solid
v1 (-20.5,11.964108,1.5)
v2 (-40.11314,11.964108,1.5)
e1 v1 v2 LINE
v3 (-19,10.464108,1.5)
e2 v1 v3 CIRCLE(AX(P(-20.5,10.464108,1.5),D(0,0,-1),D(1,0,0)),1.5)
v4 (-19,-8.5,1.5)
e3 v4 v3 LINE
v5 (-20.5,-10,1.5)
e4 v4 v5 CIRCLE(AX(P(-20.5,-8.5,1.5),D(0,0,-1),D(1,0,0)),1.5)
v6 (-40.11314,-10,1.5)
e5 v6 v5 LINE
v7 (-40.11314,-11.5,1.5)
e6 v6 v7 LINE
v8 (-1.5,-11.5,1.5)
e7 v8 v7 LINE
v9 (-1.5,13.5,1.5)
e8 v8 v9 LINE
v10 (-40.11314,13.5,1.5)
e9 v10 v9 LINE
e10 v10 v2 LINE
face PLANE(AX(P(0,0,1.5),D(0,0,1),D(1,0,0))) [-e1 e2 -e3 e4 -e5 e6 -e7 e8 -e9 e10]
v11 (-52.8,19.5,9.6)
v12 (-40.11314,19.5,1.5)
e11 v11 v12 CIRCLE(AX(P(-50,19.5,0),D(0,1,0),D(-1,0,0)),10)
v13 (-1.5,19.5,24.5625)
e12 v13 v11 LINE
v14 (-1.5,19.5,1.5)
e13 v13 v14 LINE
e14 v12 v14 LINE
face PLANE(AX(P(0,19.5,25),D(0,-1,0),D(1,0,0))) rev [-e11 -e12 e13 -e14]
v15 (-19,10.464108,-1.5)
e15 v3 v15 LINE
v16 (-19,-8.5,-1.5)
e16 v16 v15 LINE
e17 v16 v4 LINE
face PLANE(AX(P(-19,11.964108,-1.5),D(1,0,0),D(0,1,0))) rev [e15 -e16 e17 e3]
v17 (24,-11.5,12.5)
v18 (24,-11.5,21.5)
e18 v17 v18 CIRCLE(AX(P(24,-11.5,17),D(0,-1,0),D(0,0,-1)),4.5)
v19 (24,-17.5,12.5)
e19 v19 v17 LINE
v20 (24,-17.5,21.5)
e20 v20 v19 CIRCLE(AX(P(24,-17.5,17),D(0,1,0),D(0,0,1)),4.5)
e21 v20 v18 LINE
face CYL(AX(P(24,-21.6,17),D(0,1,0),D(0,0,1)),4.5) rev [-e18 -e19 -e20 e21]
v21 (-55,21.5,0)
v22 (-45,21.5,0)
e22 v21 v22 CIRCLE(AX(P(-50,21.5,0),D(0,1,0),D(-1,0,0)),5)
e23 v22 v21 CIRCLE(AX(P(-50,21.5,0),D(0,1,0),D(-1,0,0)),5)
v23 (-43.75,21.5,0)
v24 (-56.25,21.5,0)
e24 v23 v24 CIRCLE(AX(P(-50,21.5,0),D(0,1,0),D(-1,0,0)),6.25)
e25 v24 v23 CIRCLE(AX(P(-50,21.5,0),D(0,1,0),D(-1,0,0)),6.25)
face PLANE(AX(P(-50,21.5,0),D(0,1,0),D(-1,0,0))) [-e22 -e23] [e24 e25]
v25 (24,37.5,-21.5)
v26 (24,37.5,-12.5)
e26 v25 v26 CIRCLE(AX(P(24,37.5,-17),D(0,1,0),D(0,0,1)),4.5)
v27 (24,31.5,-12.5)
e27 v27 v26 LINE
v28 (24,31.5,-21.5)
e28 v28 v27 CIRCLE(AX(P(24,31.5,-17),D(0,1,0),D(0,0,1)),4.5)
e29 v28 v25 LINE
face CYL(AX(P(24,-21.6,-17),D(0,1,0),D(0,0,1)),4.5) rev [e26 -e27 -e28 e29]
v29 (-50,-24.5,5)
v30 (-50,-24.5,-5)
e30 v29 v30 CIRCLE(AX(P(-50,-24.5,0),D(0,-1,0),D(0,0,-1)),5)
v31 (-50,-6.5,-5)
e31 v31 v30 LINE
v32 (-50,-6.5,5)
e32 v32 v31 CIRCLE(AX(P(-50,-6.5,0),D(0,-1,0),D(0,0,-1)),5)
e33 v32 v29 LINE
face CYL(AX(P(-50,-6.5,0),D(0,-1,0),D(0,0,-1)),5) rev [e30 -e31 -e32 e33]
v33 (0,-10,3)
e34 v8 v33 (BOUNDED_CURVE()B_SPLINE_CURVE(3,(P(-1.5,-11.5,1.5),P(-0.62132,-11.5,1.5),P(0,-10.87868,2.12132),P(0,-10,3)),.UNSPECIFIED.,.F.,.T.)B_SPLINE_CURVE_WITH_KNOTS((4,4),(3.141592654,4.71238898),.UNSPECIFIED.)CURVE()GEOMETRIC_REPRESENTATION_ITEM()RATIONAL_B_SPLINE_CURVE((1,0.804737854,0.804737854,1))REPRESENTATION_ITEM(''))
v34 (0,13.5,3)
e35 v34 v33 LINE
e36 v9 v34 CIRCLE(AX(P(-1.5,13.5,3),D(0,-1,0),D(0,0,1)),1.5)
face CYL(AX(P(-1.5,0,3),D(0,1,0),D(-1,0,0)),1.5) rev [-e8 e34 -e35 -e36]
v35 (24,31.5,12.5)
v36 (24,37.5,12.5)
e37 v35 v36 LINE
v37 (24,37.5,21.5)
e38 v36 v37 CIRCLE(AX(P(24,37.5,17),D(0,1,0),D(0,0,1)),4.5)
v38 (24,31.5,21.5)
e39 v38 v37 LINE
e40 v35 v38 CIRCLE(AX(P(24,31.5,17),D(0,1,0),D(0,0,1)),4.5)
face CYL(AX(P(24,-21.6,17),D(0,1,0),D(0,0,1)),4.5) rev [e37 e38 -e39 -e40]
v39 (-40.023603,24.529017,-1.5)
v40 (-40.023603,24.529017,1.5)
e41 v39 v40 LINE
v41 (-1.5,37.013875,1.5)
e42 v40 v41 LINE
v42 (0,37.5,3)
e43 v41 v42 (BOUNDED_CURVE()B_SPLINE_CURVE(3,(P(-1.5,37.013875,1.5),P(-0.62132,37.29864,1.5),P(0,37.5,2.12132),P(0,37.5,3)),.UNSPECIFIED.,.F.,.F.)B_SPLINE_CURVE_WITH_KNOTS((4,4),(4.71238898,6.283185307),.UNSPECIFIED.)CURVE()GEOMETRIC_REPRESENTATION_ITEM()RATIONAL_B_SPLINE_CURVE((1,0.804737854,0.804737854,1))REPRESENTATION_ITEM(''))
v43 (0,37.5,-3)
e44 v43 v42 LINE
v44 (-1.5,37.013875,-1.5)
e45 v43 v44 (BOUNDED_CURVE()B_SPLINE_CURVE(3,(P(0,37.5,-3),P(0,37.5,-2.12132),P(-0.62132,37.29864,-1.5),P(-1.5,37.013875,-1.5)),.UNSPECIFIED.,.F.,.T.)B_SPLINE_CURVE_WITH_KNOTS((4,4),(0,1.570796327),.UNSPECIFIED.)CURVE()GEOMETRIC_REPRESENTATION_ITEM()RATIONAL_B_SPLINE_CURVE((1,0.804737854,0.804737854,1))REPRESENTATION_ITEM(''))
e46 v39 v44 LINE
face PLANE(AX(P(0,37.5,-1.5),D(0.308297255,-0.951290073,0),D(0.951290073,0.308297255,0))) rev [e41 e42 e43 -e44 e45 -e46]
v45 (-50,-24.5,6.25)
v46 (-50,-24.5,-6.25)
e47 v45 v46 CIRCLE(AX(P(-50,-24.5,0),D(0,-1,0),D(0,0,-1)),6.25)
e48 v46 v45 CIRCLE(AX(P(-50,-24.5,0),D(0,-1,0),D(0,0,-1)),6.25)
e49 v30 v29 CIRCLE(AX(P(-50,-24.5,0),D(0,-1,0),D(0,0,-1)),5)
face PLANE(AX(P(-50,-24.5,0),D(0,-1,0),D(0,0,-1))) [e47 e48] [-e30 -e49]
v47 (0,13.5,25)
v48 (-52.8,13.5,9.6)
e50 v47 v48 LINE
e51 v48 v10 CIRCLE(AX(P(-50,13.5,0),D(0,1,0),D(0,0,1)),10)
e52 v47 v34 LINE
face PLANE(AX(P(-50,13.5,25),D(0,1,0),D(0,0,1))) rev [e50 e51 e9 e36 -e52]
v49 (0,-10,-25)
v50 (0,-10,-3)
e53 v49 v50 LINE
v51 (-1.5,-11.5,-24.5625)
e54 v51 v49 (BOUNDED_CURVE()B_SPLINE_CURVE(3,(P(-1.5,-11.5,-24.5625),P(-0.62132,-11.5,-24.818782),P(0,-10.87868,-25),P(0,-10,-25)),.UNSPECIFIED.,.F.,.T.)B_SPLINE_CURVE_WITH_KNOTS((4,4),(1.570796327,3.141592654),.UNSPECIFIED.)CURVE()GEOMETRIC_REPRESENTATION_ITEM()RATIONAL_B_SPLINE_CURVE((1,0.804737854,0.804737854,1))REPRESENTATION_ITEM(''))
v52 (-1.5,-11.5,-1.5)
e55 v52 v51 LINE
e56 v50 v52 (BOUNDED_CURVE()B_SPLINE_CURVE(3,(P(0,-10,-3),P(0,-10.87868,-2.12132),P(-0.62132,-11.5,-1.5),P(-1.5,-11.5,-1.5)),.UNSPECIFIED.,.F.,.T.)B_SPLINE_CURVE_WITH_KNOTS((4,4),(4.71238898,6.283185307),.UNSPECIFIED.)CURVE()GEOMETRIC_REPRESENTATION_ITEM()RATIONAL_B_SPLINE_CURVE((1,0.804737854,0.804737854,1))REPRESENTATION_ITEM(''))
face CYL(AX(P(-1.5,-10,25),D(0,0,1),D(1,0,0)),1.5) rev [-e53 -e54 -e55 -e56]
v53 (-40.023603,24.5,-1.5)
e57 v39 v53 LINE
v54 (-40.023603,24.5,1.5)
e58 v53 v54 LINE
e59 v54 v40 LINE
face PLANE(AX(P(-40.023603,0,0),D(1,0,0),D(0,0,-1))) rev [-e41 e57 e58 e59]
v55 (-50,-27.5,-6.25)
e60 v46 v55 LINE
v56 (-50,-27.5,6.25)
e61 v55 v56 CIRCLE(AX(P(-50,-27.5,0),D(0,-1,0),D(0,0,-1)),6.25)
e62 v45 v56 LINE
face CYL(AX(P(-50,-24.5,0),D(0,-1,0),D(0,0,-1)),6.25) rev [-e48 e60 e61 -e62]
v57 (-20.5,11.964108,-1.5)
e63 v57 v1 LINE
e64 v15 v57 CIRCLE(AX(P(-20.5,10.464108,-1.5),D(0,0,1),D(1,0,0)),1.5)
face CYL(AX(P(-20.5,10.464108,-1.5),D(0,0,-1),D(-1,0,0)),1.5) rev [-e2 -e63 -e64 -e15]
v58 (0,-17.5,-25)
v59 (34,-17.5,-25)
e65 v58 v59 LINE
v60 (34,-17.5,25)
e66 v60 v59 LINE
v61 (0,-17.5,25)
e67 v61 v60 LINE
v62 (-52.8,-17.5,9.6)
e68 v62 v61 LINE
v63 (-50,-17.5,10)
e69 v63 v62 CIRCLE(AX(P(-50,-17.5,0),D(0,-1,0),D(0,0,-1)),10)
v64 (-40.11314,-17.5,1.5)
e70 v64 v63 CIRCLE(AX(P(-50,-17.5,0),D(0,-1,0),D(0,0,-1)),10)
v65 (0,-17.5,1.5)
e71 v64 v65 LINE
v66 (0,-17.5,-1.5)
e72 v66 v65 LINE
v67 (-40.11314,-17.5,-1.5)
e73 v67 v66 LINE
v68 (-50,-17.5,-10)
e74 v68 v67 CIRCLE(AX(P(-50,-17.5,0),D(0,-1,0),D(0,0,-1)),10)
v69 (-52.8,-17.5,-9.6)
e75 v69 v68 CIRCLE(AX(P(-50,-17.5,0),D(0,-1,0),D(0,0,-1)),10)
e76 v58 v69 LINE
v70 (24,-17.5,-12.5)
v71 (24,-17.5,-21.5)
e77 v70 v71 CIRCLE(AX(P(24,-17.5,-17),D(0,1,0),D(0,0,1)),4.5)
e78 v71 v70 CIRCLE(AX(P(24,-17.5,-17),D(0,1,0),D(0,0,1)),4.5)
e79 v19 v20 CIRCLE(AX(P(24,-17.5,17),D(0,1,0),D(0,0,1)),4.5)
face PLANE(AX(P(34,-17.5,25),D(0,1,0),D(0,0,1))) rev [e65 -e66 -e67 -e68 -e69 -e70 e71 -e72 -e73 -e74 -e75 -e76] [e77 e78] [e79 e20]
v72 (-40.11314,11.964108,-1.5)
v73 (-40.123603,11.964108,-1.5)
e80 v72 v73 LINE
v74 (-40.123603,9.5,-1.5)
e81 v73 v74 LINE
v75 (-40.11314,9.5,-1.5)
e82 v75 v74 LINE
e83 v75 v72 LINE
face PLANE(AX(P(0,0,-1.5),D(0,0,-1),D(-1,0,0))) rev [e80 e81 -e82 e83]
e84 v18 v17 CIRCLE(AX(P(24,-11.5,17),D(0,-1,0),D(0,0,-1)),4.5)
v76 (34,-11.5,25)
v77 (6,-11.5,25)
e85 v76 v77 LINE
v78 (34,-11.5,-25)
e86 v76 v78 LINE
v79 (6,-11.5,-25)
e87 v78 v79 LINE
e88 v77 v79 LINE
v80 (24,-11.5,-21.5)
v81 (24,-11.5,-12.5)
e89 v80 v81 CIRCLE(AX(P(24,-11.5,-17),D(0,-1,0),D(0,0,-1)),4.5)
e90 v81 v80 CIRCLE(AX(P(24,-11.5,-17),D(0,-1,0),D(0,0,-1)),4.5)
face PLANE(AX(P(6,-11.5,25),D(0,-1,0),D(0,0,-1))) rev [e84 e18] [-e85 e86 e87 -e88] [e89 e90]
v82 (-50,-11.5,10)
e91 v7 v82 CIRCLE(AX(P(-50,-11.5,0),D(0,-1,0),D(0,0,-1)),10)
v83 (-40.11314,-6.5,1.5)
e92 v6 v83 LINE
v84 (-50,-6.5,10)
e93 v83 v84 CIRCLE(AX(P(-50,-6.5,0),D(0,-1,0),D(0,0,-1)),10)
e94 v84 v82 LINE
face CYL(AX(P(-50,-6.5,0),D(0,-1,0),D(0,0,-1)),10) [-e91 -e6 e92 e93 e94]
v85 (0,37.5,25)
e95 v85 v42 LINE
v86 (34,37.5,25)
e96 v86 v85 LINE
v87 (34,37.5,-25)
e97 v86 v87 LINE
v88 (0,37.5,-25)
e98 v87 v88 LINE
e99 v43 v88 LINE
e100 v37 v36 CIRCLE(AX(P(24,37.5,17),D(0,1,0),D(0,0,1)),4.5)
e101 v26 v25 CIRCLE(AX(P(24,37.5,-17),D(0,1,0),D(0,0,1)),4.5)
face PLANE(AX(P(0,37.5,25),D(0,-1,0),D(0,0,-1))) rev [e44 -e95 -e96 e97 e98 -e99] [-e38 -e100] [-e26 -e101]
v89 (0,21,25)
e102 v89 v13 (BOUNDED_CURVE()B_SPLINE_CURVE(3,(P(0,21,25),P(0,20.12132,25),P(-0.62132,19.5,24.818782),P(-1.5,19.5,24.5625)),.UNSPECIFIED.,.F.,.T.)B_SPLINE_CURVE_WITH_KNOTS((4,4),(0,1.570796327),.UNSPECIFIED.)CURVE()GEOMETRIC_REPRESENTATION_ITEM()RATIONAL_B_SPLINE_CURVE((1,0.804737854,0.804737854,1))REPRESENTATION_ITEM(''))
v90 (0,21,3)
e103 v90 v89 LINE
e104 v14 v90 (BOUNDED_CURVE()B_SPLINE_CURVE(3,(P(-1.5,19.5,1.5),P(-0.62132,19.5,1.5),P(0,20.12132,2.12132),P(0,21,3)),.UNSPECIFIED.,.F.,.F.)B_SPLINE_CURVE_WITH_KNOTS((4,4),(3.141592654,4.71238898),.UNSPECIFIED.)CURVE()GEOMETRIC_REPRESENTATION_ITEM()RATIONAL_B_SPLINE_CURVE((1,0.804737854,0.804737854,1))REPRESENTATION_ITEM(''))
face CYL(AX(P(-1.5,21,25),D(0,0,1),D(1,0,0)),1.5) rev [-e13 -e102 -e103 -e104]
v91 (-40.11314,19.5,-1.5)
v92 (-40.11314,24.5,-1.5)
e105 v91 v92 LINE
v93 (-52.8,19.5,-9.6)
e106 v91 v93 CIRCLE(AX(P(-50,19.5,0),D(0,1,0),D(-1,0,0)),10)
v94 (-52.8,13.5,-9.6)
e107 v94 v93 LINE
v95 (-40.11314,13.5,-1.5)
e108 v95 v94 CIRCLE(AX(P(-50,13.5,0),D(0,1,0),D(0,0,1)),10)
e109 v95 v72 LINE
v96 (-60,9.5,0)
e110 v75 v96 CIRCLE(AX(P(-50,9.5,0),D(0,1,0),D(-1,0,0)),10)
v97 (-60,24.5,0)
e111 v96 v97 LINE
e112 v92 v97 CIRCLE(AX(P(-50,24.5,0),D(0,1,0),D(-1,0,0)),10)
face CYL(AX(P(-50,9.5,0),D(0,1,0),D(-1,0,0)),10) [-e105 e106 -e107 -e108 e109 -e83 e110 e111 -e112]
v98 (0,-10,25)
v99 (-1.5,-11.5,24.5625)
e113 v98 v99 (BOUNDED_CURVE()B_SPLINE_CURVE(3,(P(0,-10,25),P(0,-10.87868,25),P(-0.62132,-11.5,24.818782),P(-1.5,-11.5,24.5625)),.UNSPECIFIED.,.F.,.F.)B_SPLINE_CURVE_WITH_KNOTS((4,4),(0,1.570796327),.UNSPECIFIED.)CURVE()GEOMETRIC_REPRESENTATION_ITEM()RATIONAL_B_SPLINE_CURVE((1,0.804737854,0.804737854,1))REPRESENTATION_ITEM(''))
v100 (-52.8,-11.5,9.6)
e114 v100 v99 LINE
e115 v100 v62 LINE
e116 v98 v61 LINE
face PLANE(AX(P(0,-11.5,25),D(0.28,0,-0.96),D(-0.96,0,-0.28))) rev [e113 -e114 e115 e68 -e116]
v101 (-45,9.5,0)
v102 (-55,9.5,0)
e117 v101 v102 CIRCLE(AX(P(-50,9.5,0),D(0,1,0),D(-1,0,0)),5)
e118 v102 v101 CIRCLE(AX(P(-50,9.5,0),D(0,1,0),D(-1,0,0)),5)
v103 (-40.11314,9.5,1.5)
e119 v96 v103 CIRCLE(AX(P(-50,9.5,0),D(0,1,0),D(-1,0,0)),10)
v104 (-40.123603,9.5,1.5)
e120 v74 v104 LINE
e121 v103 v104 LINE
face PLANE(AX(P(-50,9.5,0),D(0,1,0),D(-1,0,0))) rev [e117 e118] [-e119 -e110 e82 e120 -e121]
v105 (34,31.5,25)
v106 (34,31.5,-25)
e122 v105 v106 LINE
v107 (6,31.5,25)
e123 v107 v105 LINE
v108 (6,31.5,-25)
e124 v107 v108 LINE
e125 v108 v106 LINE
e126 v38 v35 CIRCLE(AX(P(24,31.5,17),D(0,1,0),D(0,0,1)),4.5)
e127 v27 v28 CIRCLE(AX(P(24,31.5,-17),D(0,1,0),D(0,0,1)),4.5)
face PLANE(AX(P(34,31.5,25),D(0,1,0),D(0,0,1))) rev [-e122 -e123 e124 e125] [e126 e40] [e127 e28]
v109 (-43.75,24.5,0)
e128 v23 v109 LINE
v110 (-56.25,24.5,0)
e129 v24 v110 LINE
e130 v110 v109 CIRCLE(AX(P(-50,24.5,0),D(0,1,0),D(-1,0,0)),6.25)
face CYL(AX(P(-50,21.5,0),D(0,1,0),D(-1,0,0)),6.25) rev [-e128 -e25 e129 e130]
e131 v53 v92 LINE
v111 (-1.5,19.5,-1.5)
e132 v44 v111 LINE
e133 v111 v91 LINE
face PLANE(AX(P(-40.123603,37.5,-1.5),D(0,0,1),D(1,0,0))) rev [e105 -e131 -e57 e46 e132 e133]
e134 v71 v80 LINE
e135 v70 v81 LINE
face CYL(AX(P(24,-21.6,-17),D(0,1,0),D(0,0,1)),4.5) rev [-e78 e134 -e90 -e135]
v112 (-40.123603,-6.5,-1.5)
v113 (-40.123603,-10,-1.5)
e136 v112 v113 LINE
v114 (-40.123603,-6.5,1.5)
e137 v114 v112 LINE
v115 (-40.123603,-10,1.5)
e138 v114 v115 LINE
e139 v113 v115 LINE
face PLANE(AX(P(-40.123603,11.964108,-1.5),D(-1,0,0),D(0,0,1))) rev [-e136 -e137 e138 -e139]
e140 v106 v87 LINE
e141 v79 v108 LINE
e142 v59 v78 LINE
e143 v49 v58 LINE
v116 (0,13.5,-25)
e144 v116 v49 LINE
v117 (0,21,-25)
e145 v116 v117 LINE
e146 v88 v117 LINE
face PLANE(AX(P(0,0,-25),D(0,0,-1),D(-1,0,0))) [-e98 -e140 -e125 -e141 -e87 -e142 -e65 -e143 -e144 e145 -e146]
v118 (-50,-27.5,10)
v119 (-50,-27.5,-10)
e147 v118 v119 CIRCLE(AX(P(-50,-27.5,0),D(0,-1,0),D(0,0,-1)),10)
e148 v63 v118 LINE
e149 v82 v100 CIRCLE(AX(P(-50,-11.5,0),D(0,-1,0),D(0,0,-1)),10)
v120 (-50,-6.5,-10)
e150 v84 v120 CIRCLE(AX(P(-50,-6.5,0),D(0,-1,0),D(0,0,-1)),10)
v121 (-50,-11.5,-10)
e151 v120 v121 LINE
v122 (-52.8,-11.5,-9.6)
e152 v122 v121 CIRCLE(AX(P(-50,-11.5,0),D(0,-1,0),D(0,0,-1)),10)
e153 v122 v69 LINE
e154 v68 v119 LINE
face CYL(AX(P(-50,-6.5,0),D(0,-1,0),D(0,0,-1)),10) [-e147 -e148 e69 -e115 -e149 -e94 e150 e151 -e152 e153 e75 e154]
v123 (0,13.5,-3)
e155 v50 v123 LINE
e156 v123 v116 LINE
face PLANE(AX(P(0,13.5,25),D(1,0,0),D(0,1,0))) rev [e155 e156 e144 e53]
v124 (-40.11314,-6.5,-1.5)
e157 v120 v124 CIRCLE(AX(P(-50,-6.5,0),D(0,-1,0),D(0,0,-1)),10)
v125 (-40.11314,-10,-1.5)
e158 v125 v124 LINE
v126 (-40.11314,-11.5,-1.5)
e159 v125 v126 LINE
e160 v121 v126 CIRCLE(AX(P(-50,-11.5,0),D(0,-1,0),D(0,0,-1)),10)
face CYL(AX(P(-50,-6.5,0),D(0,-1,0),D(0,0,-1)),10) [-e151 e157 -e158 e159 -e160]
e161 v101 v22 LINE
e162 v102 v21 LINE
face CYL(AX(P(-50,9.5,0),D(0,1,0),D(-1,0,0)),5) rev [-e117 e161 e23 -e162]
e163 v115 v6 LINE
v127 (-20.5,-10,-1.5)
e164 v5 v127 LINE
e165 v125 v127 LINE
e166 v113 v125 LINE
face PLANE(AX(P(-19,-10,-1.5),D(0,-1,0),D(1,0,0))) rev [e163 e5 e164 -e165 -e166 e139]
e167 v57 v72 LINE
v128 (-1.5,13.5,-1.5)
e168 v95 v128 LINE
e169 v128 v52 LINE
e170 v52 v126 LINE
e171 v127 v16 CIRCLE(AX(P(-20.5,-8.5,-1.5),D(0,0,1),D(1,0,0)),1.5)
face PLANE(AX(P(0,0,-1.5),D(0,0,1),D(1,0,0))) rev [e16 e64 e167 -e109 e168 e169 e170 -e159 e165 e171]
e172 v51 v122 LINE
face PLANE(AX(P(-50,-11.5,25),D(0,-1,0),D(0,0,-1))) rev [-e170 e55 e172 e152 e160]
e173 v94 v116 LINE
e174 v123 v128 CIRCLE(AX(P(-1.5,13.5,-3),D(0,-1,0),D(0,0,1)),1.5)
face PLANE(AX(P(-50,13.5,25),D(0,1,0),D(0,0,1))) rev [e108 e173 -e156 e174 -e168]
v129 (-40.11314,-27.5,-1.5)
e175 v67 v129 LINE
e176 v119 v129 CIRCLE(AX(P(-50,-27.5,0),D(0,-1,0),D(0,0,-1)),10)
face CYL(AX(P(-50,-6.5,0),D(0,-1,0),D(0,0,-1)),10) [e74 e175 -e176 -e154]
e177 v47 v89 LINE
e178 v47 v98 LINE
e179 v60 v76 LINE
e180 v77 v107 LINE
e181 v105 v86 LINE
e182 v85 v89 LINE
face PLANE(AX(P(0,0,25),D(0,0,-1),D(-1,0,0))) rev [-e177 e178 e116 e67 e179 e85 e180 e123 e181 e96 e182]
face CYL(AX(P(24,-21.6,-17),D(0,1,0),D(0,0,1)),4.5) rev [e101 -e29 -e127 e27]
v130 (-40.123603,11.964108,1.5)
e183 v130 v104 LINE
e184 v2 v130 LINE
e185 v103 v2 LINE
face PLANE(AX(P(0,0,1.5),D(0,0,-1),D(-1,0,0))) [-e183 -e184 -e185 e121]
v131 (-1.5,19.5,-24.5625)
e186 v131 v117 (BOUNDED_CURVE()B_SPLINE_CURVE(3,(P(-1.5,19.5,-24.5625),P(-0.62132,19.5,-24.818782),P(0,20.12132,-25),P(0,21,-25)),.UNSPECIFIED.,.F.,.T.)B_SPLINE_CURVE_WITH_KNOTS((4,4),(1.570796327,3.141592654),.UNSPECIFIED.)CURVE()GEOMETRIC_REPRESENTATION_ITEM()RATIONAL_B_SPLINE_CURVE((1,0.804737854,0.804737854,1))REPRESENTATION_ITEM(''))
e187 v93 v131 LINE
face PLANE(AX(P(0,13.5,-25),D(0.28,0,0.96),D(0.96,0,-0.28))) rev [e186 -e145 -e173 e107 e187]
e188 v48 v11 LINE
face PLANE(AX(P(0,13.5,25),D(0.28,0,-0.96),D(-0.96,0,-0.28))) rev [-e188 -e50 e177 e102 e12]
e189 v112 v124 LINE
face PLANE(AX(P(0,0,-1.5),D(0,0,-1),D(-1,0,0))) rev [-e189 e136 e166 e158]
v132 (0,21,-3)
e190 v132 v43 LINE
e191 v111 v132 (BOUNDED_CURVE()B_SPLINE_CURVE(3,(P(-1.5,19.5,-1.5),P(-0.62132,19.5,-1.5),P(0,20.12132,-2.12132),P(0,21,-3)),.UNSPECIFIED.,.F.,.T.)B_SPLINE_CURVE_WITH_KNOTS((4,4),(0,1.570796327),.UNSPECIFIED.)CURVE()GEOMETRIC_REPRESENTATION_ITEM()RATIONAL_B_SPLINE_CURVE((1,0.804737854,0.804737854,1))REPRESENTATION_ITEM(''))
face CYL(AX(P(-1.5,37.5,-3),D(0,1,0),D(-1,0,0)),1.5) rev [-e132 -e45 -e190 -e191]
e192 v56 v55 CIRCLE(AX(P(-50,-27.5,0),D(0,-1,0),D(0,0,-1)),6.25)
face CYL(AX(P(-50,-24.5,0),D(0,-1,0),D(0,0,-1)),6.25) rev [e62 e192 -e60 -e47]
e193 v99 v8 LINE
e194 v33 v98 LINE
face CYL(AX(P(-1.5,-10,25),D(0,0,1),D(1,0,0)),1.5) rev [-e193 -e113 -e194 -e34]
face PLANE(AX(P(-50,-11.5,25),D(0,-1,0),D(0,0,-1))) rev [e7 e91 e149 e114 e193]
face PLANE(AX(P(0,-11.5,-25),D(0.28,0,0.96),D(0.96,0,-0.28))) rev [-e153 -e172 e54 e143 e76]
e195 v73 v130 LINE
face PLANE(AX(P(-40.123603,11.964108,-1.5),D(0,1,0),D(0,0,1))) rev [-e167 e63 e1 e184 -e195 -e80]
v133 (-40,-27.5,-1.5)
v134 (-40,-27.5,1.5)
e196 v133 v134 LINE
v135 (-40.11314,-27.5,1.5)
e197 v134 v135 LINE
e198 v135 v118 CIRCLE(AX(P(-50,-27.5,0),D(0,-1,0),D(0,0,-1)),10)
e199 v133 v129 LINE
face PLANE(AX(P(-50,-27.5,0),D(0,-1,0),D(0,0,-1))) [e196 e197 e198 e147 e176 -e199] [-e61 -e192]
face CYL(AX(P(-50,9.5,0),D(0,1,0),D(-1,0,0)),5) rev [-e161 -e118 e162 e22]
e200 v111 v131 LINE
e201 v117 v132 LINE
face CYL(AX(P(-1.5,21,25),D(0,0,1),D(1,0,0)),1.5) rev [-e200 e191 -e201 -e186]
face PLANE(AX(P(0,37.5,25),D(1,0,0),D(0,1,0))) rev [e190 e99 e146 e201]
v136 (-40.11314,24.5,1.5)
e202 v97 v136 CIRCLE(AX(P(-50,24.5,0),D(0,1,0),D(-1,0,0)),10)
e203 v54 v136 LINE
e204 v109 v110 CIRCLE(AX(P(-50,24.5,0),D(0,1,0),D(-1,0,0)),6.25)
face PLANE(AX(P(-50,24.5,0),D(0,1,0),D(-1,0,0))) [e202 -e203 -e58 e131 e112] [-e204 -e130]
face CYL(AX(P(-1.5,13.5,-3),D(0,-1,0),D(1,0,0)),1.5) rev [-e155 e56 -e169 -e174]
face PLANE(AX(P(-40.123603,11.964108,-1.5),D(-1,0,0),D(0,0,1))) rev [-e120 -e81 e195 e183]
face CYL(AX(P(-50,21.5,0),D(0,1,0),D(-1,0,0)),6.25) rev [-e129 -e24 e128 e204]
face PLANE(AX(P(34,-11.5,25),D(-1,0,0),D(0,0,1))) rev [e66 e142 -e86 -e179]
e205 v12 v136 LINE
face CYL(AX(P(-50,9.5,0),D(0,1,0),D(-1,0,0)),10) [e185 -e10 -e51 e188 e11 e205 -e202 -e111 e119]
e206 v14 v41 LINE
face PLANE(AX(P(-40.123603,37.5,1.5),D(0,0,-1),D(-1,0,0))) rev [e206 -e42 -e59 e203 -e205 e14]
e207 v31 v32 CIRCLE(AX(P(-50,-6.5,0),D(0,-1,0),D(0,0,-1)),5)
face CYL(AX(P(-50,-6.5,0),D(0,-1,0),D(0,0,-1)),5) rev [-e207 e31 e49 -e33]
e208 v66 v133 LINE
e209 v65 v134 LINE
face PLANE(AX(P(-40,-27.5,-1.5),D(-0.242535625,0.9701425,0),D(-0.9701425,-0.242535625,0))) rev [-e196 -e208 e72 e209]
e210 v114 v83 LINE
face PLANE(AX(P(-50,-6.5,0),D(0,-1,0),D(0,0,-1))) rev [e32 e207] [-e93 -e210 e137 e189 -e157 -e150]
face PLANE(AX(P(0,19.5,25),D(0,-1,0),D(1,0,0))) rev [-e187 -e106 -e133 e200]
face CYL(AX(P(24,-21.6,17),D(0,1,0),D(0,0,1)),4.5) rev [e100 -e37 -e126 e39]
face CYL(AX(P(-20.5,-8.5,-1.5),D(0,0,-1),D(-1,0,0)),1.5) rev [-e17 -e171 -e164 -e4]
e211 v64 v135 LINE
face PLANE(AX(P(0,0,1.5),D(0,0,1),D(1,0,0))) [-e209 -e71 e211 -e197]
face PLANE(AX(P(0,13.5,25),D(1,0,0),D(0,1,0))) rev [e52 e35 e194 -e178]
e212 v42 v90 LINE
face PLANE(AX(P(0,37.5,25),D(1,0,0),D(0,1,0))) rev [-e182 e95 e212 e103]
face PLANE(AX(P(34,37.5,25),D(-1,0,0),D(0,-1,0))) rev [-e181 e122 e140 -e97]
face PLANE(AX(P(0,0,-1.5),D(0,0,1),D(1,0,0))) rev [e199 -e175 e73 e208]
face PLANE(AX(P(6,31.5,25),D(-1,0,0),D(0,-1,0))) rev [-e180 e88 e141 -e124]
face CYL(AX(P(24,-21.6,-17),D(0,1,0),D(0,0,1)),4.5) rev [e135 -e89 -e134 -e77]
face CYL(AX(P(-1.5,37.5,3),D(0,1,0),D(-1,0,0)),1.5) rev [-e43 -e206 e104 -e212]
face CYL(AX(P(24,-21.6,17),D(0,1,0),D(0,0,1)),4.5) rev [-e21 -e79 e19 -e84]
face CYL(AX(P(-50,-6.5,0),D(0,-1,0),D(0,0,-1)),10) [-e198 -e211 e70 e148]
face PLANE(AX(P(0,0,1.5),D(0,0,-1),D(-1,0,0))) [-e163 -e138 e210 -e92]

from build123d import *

# Parameters (mm, degrees)
U_CHANNEL_BASE_DEPTH             = 25
UPPER_LUG_BOSS_SKETCH_20_R       = 10
UPPER_LUG_BOSS_20_DEPTH          = 10
UPPER_START                      = 5
UPPER_LUG_PAD_SKETCH_R           = 10
UPPER_LUG_PAD_DEPTH              = 5
UPPER_COUNTERBORE_SKETCH_12_5_R  = 6.25
UPPER_COUNTERBORE_12_5_DEPTH     = 3
UPPER_LUG_HOLE_SKETCH_10_R       = 5
UPPER_LUG_HOLE_10_DEPTH          = 12
LOWER_START                      = -11
LOWER_LUG_PAD_SKETCH_R           = 10
LOWER_LUG_PAD_DEPTH              = 11
LOWER_LUG_BOSS_SKETCH_20_R       = 10
LOWER_LUG_BOSS_20_DEPTH          = 10
LOWER_START_2                    = -3
LOWER_COUNTERBORE_SKETCH_12_5_R  = 6.25
LOWER_COUNTERBORE_12_5_DEPTH     = 3
LOWER_START_3                    = -18
LOWER_LUG_HOLE_SKETCH_10_R       = 5
LOWER_LUG_HOLE_10_DEPTH          = 18
UPPER_GUSSET_DEPTH               = 6
UPPER_GUSSET_TRIM_DEPTH          = 6
LOWER_GUSSET_DEPTH               = 6
LOWER_GUSSET_TRIM_DEPTH          = 6
BACK_PLATE_DEPTH                 = 1.5
BACK_PLATE_LOWER_RELIEF_DEPTH    = 3
LOWER_LUG_RELIEF_SKETCH_W        = 3
LOWER_LUG_RELIEF_SKETCH_H        = 5
LOWER_LUG_RELIEF_DEPTH           = 3
BACK_PLATE_UPPER_RELIEF_SKETCH_W = 40.123603225
BACK_PLATE_UPPER_RELIEF_SKETCH_H = 13
BACK_PLATE_UPPER_RELIEF_DEPTH    = 3
BACK_PLATE_EDGE_TRIM_SKETCH_W    = 21.123603225
BACK_PLATE_EDGE_TRIM_SKETCH_H    = 21.964107992
BACK_PLATE_EDGE_TRIM_DEPTH       = 3
WEB_SKETCH_W                     = 40.123603225
WEB_SKETCH_H                     = 3
WEB_DEPTH                        = 18
WEB_CHAMFER_CUT_DEPTH            = 3
WEB_FACE_TRIM_SKETCH_W           = 3
WEB_FACE_TRIM_SKETCH_H           = 13
WEB_FACE_TRIM_0_1_DEPTH          = 0.1
FLANGE_MOUNTING_HOLES_SKETCH_R   = 4.5
FLANGE_MOUNTING_HOLES_4X_DEPTH   = 59.1
EDGE_FILLET_R1_5_R               = 1.5


with BuildPart() as part:
    # U-Channel Profile Sketch → U-Channel Base (new, symmetric)
    with BuildSketch(Plane.XY):
        Polygon((0, 37.5), (0, 19.5), (-50, 19.5), (-50, 13.5), (0, 13.5), (0, -11.5), (-50, -11.5), (-50, -17.5), (0, -17.5), (34, -17.5), (34, -11.5), (6, -11.5), (6, 31.5), (34, 31.5), (34, 37.5), align=None)
    extrude(amount=U_CHANNEL_BASE_DEPTH, both=True)

    # Upper Lug Boss Sketch Ø20 → Upper Lug Boss Ø20 (add)
    with BuildSketch(Plane(origin=(0, 19.5, 0), x_dir=(1, 0, 0), z_dir=(0, 1, 0))):
        with Locations(Location((-50, 0, 0), (0, 0, 180))):
            Circle(UPPER_LUG_BOSS_SKETCH_20_R)
    extrude(amount=-UPPER_LUG_BOSS_20_DEPTH)

    # Upper Lug Pad Sketch → Upper Lug Pad (add)
    with BuildSketch(Plane(origin=(0, 19.5, 0), x_dir=(1, 0, 0), z_dir=(0, 1, 0)).offset(UPPER_START)):
        with Locations(Location((-50, 0, 0), (0, 0, 180))):
            Circle(UPPER_LUG_PAD_SKETCH_R)
    extrude(amount=-UPPER_LUG_PAD_DEPTH)

    # Upper Counterbore Sketch Ø12.5 → Upper Counterbore Ø12.5 (cut)
    with BuildSketch(Plane(origin=(0, 24.5, 0), x_dir=(1, 0, 0), z_dir=(0, 1, 0))):
        with Locations(Location((-50, 0, 0), (0, 0, 180))):
            Circle(UPPER_COUNTERBORE_SKETCH_12_5_R)
    extrude(amount=-UPPER_COUNTERBORE_12_5_DEPTH, mode=Mode.SUBTRACT)

    # Upper Lug Hole Sketch Ø10 → Upper Lug Hole Ø10 (cut)
    with BuildSketch(Plane(origin=(0, 21.5, 0), x_dir=(1, 0, 0), z_dir=(0, 1, 0))):
        with Locations(Location((-50, 0, 0), (0, 0, 180))):
            Circle(UPPER_LUG_HOLE_SKETCH_10_R)
    extrude(amount=-UPPER_LUG_HOLE_10_DEPTH, mode=Mode.SUBTRACT)

    # Lower Lug Pad Sketch → Lower Lug Pad (add)
    with BuildSketch(Plane.XZ.offset(17.5).offset(LOWER_START)):
        with Locations(Location((-50, 0, 0), (0, 0, 180))):
            Circle(LOWER_LUG_PAD_SKETCH_R)
    extrude(amount=LOWER_LUG_PAD_DEPTH)

    # Lower Lug Boss Sketch Ø20 → Lower Lug Boss Ø20 (add)
    with BuildSketch(Plane.XZ.offset(17.5)):
        with Locations(Location((-50, 0, 0), (0, 0, 180))):
            Circle(LOWER_LUG_BOSS_SKETCH_20_R)
    extrude(amount=LOWER_LUG_BOSS_20_DEPTH)

    # Lower Counterbore Sketch Ø12.5 → Lower Counterbore Ø12.5 (cut)
    with BuildSketch(Plane.XZ.offset(27.5).offset(LOWER_START_2)):
        with Locations(Location((-50, 0, 0), (0, 0, 180))):
            Circle(LOWER_COUNTERBORE_SKETCH_12_5_R)
    extrude(amount=LOWER_COUNTERBORE_12_5_DEPTH, mode=Mode.SUBTRACT)

    # Lower Lug Hole Sketch Ø10 → Lower Lug Hole Ø10 (cut)
    with BuildSketch(Plane.XZ.offset(24.5).offset(LOWER_START_3)):
        with Locations(Location((-50, 0, 0), (0, 0, 180))):
            Circle(LOWER_LUG_HOLE_SKETCH_10_R)
    extrude(amount=LOWER_LUG_HOLE_10_DEPTH, mode=Mode.SUBTRACT)

    # Upper Gusset Sketch → Upper Gusset (add)
    with BuildSketch(Plane(origin=(0, 19.5, 0), x_dir=(1, 0, 0), z_dir=(0, 1, 0))):
        Polygon((0, 25), (-50, 10.416666667), (-50, 10), (-52.8, 9.6), (-52.8, 25), align=None)
        Polygon((-52.8, -9.6), (-52.8, -25), (0, -25), (-50, -10.416666667), (-50, -10), align=None)
    extrude(amount=-UPPER_GUSSET_DEPTH)

    # Upper Gusset Trim Sketch → Upper Gusset Trim (cut)
    with BuildSketch(Plane(origin=(0, 19.5, 0), x_dir=(1, 0, 0), z_dir=(0, 1, 0))):
        Polygon((0, 25), (-52.8, 9.6), (-52.8, 25), align=None)
        Polygon((0, -25), (-52.8, -9.6), (-52.8, -25), align=None)
    extrude(amount=-UPPER_GUSSET_TRIM_DEPTH, mode=Mode.SUBTRACT)

    # Lower Gusset Sketch → Lower Gusset (add)
    with BuildSketch(Plane.XZ.offset(17.5)):
        Polygon((0, 25), (-50, 10.416666667), (-50, 10), (-52.8, 9.6), (-52.8, 25), align=None)
        Polygon((0, -25), (-50, -10.416666667), (-50, -10), (-52.8, -9.6), (-52.8, -25), align=None)
    extrude(amount=-LOWER_GUSSET_DEPTH)

    # Lower Gusset Trim Sketch → Lower Gusset Trim (cut)
    with BuildSketch(Plane.XZ.offset(17.5)):
        Polygon((0, 25), (-52.8, 9.6), (-52.8, 25), align=None)
        Polygon((0, -25), (-52.8, -9.6), (-52.8, -25), align=None)
    extrude(amount=-LOWER_GUSSET_TRIM_DEPTH, mode=Mode.SUBTRACT)


with BuildPart() as body_2:
    # Back Plate Sketch → Back Plate (new, symmetric)
    with BuildSketch(Plane.XY):
        Polygon((0, 0), (0, 32.5), (-40.123603225, 32.5), (-40.123603225, -32.5), (0, -32.5), align=None)
    extrude(amount=BACK_PLATE_DEPTH, both=True)

    # Back Plate Lower Relief Sketch → Back Plate Lower Relief (cut)
    with BuildSketch(Plane.XY.offset(1.5)):
        Polygon((-40, -27.5), (0, -17.5), (0, -32.5), (-40.123603225, -32.5), align=None)
    extrude(amount=-BACK_PLATE_LOWER_RELIEF_DEPTH, mode=Mode.SUBTRACT)

    # Lower Lug Relief Sketch → Lower Lug Relief (cut)
    with BuildSketch(Plane.ZY.offset(40.123603225)):
        with Locations((0, -30)):
            Rectangle(LOWER_LUG_RELIEF_SKETCH_W, LOWER_LUG_RELIEF_SKETCH_H)
    extrude(amount=-LOWER_LUG_RELIEF_DEPTH, mode=Mode.SUBTRACT)


with BuildPart() as back_plate_upper_relief_tool:
    # Back Plate Upper Relief Sketch → Back Plate Upper Relief (new body)
    with BuildSketch(Plane.XY.offset(1.5)):
        with Locations((-20.061801613, 26)):
            Rectangle(BACK_PLATE_UPPER_RELIEF_SKETCH_W, BACK_PLATE_UPPER_RELIEF_SKETCH_H)
    extrude(amount=-BACK_PLATE_UPPER_RELIEF_DEPTH)


with BuildPart() as part_1:
    add(part.part)

    # Back Plate Upper Relief: cut by back_plate_upper_relief_tool
    add(back_plate_upper_relief_tool.part, mode=Mode.SUBTRACT)


with BuildPart() as body_2_1:
    add(body_2.part)

    # Back Plate Upper Relief: cut by back_plate_upper_relief_tool
    add(back_plate_upper_relief_tool.part, mode=Mode.SUBTRACT)


with BuildPart() as back_plate_edge_trim_tool:
    # Back Plate Edge Trim Sketch → Back Plate Edge Trim (new body)
    with BuildSketch(Plane.XY.offset(1.5)):
        with Locations((-29.561801613, 0.982053996)):
            Rectangle(BACK_PLATE_EDGE_TRIM_SKETCH_W, BACK_PLATE_EDGE_TRIM_SKETCH_H)
    extrude(amount=-BACK_PLATE_EDGE_TRIM_DEPTH)


with BuildPart() as part_2:
    add(part_1.part)

    # Back Plate Edge Trim: cut by back_plate_edge_trim_tool
    add(back_plate_edge_trim_tool.part, mode=Mode.SUBTRACT)



with BuildPart() as body_2_2:
    add(body_2_1.part)

    # Back Plate Edge Trim: cut by back_plate_edge_trim_tool
    add(back_plate_edge_trim_tool.part, mode=Mode.SUBTRACT)


with BuildPart() as part_3:
    add(part_2.part)

    add(body_2_2.part)  # Web merges body 2
    # Web Sketch → Web (add)
    with BuildSketch(Plane(origin=(0, 19.5, 0), x_dir=(1, 0, 0), z_dir=(0, 1, 0))):
        with Locations((-20.061801613, 0)):
            Rectangle(WEB_SKETCH_W, WEB_SKETCH_H)
    extrude(amount=WEB_DEPTH)

    # Web Chamfer Cut Sketch → Web Chamfer Cut (cut)
    with BuildSketch(Plane.XY.offset(1.5)):
        Polygon((0, 37.5), (-40.113140033, 24.5), (-40.123603225, 37.5), align=None)
    extrude(amount=-WEB_CHAMFER_CUT_DEPTH, mode=Mode.SUBTRACT)

    # Web Face Trim Sketch → Web Face Trim 0.1 (cut)
    with BuildSketch(Plane.ZY.offset(40.123603225)):
        with Locations((0, 31)):
            Rectangle(WEB_FACE_TRIM_SKETCH_W, WEB_FACE_TRIM_SKETCH_H)
    extrude(amount=-WEB_FACE_TRIM_0_1_DEPTH, mode=Mode.SUBTRACT)

    # Flange Mounting Holes Sketch → Flange Mounting Holes 4x (cut)
    with BuildSketch(Plane(origin=(0, 37.5, 0), x_dir=(1, 0, 0), z_dir=(0, 1, 0))):
        with Locations(Location((24, 17, 0), (0, 0, 270))):
            Circle(FLANGE_MOUNTING_HOLES_SKETCH_R)
        with Locations(Location((24, -17, 0), (0, 0, 270))):
            Circle(FLANGE_MOUNTING_HOLES_SKETCH_R)
    extrude(amount=-FLANGE_MOUNTING_HOLES_4X_DEPTH, mode=Mode.SUBTRACT)

    # Edge Fillet R1.5
    edge_fillet_r1_5_edges = [part_3.edges().sort_by_distance(p)[0] for p in [
        (0, -11.5, 13.25),
        (0, 19.5, 13.25),
        (0, 19.5, -13.25),
        (0, 28.5, 1.5),
        (0, 28.5, -1.5),
        (0, -11.5, -13.25),
        (0, 1, -1.5),
        (0, 1, 1.5),
        (-19, 11.964107992, 0),
        (-19, -10, 0),
    ]]
    fillet(edge_fillet_r1_5_edges, radius=EDGE_FILLET_R1_5_R)


solid = part_3.part
